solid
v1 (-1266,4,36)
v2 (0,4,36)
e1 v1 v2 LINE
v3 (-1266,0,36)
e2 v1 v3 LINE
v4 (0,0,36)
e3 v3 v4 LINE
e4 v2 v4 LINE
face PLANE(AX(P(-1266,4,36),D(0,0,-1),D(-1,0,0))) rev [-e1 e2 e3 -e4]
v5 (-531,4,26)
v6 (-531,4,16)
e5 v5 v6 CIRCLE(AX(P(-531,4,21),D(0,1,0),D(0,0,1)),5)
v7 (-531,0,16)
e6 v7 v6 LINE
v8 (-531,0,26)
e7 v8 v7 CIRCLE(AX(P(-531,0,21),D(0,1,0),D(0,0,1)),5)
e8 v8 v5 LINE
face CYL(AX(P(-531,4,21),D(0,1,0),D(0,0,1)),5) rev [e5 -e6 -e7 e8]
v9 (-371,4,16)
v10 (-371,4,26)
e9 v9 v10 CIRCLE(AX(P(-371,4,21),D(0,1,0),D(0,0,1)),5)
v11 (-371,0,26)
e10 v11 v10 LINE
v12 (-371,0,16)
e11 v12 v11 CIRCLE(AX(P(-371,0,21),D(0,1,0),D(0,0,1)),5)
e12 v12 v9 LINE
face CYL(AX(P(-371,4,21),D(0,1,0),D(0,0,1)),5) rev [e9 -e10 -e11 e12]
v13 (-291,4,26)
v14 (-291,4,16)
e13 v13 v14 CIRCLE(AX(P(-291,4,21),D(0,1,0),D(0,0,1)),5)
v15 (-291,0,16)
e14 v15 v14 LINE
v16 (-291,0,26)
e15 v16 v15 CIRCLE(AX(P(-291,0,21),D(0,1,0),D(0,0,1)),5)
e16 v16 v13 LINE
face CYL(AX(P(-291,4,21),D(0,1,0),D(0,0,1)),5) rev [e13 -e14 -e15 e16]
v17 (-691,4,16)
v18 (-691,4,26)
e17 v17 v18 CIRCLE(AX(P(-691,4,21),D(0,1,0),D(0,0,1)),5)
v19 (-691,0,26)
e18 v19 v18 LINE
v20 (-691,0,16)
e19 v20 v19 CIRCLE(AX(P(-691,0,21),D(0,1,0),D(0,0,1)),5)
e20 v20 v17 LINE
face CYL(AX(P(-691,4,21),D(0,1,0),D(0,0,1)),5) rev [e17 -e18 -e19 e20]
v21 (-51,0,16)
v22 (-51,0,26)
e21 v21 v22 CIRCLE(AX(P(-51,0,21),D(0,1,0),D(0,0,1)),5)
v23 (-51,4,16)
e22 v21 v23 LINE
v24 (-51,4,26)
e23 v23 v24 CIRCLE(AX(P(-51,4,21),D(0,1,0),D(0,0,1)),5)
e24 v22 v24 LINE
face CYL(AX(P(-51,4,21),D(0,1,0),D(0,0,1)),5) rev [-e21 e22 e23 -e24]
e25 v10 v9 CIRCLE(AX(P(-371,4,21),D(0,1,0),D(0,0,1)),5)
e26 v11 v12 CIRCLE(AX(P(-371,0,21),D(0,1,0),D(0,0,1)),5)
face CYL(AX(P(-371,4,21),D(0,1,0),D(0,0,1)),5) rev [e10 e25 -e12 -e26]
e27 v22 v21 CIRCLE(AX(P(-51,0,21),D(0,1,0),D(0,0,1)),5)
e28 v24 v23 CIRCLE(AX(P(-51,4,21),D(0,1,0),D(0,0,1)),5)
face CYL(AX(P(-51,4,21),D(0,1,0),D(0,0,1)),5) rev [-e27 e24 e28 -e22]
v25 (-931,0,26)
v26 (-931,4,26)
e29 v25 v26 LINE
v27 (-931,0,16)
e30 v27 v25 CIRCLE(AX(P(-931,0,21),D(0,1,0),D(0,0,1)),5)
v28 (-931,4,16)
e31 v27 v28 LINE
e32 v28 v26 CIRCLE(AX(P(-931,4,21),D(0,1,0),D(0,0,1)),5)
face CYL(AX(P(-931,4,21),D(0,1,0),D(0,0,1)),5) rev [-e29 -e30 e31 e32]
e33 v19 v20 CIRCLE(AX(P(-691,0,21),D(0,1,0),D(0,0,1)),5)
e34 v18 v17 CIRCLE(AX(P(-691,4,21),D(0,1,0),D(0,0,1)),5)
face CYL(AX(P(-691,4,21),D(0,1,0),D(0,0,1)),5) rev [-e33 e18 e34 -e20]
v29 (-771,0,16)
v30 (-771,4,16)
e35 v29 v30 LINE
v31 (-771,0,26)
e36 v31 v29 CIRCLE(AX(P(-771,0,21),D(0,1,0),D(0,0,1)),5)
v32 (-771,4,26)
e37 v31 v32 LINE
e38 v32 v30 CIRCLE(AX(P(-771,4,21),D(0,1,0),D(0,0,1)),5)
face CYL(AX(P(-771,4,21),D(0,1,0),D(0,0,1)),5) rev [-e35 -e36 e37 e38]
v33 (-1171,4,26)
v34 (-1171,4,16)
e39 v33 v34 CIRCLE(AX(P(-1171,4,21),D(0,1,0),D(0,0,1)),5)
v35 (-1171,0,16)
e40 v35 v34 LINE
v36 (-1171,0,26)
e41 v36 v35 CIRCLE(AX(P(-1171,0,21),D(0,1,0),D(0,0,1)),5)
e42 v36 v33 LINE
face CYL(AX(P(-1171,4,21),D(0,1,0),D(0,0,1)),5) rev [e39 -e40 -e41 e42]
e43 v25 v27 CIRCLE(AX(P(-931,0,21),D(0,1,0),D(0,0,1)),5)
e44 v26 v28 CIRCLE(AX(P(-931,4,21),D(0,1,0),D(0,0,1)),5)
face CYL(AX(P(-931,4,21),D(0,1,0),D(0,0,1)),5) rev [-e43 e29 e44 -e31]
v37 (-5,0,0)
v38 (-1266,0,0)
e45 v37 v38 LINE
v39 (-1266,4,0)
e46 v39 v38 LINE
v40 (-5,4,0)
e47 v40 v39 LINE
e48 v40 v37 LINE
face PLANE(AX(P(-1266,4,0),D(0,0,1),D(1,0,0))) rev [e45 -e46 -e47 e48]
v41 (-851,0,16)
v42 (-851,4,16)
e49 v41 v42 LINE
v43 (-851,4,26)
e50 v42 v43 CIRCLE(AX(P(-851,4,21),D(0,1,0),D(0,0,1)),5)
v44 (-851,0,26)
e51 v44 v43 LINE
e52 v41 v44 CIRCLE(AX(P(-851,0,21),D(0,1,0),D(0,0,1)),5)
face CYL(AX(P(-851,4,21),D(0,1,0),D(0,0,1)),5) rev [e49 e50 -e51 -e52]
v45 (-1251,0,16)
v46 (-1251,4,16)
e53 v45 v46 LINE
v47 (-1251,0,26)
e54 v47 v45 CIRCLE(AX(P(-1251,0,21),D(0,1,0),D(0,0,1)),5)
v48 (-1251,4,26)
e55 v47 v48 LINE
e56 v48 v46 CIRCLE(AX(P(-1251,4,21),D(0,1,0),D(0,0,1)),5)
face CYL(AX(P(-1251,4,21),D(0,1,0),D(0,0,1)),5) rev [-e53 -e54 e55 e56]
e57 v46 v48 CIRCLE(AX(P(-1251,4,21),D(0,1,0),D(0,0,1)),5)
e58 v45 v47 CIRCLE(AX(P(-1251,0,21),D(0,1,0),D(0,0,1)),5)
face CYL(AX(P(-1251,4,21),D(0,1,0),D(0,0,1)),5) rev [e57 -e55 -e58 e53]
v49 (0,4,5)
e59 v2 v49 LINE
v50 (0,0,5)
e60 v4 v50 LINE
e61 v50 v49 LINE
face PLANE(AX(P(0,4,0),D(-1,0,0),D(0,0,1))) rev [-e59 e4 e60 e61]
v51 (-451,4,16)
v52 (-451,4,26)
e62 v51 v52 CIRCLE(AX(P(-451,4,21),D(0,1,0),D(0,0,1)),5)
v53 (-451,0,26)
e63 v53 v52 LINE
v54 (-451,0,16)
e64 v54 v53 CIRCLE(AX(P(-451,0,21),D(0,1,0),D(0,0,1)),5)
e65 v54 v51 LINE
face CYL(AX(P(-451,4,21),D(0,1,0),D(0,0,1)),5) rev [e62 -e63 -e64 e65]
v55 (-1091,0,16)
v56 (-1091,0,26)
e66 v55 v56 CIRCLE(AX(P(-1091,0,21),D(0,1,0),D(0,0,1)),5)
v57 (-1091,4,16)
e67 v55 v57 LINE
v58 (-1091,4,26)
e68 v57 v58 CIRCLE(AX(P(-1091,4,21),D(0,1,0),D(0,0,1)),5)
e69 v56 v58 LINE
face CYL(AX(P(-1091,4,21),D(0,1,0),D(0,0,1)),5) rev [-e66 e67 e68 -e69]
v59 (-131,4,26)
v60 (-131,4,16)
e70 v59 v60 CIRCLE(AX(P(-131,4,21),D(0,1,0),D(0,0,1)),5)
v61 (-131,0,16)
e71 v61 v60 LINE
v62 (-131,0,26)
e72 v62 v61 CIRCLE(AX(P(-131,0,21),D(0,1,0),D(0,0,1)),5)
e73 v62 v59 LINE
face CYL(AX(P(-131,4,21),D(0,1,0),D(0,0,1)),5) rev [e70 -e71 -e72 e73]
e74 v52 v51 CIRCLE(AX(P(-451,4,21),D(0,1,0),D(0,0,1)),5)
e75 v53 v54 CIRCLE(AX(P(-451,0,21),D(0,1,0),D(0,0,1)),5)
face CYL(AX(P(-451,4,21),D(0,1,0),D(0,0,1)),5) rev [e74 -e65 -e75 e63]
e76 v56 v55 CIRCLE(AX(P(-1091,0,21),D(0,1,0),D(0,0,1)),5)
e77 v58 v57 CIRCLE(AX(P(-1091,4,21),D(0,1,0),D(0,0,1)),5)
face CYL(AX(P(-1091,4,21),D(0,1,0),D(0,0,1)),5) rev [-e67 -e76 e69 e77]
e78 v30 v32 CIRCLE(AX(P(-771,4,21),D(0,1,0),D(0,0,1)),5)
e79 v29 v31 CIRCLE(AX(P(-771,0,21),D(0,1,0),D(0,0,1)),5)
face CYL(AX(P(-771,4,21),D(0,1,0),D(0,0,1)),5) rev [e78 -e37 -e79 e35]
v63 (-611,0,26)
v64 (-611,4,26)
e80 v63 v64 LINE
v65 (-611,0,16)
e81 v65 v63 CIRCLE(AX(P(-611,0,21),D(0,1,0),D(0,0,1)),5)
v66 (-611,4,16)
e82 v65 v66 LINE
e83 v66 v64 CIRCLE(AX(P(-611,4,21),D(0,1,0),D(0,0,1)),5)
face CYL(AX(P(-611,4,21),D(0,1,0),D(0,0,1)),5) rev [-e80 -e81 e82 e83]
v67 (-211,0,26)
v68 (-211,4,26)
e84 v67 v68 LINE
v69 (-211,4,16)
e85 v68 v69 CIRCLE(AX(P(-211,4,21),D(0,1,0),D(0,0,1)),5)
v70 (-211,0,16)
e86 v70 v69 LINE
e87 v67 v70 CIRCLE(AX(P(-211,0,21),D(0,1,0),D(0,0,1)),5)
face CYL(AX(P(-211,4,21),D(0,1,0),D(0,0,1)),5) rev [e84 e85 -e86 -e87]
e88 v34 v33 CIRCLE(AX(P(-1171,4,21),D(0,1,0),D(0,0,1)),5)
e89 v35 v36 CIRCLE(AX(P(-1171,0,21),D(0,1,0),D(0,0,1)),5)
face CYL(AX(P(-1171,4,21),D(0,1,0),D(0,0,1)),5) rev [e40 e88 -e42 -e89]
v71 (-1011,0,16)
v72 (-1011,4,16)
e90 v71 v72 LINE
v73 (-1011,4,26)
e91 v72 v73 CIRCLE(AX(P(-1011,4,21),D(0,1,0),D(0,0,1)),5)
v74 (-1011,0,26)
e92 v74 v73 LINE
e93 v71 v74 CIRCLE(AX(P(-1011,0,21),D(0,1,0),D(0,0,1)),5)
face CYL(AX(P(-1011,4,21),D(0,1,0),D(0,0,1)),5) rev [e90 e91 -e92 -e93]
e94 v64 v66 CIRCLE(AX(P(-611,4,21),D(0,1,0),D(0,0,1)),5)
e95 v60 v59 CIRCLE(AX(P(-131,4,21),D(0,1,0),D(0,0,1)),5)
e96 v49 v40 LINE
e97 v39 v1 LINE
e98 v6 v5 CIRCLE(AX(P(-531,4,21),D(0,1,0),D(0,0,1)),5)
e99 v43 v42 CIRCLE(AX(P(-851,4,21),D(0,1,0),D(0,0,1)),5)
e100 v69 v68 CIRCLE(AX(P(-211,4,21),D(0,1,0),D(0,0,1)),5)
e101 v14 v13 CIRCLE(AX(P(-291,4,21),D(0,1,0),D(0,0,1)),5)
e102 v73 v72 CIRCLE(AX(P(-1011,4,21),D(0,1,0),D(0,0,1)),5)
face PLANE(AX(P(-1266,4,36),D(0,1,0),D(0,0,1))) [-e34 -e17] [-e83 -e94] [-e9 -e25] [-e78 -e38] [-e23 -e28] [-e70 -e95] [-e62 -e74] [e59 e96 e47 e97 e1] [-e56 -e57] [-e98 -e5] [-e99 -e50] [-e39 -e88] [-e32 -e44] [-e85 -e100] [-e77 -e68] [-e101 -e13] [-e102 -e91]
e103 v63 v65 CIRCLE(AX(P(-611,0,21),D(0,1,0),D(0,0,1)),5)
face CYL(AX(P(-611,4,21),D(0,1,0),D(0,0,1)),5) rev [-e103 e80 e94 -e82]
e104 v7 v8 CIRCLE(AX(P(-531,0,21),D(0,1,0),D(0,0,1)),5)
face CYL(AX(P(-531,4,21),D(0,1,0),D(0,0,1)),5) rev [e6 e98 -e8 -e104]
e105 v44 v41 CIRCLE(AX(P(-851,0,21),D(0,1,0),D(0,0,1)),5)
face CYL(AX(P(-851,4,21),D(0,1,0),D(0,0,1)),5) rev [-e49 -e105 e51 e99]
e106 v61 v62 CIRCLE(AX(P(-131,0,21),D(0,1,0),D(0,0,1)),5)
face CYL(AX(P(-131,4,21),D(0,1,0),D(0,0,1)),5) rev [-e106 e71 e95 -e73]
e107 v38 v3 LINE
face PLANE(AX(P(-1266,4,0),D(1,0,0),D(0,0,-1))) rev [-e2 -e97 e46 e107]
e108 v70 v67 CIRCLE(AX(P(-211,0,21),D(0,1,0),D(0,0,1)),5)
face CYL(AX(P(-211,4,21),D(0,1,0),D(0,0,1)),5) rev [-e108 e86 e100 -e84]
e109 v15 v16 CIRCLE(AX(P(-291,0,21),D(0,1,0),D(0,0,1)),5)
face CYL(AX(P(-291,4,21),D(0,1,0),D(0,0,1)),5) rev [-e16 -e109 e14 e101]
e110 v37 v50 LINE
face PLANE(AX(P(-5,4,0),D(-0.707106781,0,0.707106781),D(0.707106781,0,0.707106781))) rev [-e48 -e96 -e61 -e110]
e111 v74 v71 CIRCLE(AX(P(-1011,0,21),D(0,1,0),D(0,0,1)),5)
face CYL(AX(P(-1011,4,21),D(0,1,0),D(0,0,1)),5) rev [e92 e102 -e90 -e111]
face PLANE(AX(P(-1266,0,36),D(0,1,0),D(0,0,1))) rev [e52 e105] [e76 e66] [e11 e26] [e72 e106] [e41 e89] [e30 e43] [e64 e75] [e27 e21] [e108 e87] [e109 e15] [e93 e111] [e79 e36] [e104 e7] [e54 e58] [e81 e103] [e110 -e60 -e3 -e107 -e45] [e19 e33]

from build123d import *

# Parameters (mm, degrees)
SKETCH_1_W              = 1266
SKETCH_1_H              = 36
EXTRUDE_1_DEPTH         = 4
CHAMFER_1_SIZE          = 5
HOLE_WIZARD_10_0_10_1_D = 10
PATTERN_LINEAR_1_COUNT  = 16
PATTERN_LINEAR_1_PITCH  = 80


with BuildPart() as part:
    # 草图1 → 凸台-拉伸1 (new body)
    with BuildSketch(Plane(origin=(0, 0, 0), x_dir=(1, 0, 0), z_dir=(0, 1, 0))):
        with Locations((-633, -18)):
            Rectangle(SKETCH_1_W, SKETCH_1_H)
    extrude(amount=EXTRUDE_1_DEPTH)

    # 倒角1
    chamfer_1_edges = [part.edges().sort_by_distance(p)[0] for p in [
        (0, 2, 0),
    ]]
    chamfer(chamfer_1_edges, length=CHAMFER_1_SIZE)

    # Ø10.0 (10) 直径孔1 (through all)
    with Locations(Plane(origin=(0, 4, 0), x_dir=(-1, 0, 0), z_dir=(0, 1, 0))):
        with Locations((1251, 21)):
            hole_wizard_10_0_10_1 = Hole(HOLE_WIZARD_10_0_10_1_D / 2)

    # 阵列(线性)1: Ø10.0 (10) 直径孔1 ×16
    with Locations(*[(i * PATTERN_LINEAR_1_PITCH, 0, 0) for i in range(1, PATTERN_LINEAR_1_COUNT)]):
        add(hole_wizard_10_0_10_1, mode=Mode.SUBTRACT)


solid = part.part
